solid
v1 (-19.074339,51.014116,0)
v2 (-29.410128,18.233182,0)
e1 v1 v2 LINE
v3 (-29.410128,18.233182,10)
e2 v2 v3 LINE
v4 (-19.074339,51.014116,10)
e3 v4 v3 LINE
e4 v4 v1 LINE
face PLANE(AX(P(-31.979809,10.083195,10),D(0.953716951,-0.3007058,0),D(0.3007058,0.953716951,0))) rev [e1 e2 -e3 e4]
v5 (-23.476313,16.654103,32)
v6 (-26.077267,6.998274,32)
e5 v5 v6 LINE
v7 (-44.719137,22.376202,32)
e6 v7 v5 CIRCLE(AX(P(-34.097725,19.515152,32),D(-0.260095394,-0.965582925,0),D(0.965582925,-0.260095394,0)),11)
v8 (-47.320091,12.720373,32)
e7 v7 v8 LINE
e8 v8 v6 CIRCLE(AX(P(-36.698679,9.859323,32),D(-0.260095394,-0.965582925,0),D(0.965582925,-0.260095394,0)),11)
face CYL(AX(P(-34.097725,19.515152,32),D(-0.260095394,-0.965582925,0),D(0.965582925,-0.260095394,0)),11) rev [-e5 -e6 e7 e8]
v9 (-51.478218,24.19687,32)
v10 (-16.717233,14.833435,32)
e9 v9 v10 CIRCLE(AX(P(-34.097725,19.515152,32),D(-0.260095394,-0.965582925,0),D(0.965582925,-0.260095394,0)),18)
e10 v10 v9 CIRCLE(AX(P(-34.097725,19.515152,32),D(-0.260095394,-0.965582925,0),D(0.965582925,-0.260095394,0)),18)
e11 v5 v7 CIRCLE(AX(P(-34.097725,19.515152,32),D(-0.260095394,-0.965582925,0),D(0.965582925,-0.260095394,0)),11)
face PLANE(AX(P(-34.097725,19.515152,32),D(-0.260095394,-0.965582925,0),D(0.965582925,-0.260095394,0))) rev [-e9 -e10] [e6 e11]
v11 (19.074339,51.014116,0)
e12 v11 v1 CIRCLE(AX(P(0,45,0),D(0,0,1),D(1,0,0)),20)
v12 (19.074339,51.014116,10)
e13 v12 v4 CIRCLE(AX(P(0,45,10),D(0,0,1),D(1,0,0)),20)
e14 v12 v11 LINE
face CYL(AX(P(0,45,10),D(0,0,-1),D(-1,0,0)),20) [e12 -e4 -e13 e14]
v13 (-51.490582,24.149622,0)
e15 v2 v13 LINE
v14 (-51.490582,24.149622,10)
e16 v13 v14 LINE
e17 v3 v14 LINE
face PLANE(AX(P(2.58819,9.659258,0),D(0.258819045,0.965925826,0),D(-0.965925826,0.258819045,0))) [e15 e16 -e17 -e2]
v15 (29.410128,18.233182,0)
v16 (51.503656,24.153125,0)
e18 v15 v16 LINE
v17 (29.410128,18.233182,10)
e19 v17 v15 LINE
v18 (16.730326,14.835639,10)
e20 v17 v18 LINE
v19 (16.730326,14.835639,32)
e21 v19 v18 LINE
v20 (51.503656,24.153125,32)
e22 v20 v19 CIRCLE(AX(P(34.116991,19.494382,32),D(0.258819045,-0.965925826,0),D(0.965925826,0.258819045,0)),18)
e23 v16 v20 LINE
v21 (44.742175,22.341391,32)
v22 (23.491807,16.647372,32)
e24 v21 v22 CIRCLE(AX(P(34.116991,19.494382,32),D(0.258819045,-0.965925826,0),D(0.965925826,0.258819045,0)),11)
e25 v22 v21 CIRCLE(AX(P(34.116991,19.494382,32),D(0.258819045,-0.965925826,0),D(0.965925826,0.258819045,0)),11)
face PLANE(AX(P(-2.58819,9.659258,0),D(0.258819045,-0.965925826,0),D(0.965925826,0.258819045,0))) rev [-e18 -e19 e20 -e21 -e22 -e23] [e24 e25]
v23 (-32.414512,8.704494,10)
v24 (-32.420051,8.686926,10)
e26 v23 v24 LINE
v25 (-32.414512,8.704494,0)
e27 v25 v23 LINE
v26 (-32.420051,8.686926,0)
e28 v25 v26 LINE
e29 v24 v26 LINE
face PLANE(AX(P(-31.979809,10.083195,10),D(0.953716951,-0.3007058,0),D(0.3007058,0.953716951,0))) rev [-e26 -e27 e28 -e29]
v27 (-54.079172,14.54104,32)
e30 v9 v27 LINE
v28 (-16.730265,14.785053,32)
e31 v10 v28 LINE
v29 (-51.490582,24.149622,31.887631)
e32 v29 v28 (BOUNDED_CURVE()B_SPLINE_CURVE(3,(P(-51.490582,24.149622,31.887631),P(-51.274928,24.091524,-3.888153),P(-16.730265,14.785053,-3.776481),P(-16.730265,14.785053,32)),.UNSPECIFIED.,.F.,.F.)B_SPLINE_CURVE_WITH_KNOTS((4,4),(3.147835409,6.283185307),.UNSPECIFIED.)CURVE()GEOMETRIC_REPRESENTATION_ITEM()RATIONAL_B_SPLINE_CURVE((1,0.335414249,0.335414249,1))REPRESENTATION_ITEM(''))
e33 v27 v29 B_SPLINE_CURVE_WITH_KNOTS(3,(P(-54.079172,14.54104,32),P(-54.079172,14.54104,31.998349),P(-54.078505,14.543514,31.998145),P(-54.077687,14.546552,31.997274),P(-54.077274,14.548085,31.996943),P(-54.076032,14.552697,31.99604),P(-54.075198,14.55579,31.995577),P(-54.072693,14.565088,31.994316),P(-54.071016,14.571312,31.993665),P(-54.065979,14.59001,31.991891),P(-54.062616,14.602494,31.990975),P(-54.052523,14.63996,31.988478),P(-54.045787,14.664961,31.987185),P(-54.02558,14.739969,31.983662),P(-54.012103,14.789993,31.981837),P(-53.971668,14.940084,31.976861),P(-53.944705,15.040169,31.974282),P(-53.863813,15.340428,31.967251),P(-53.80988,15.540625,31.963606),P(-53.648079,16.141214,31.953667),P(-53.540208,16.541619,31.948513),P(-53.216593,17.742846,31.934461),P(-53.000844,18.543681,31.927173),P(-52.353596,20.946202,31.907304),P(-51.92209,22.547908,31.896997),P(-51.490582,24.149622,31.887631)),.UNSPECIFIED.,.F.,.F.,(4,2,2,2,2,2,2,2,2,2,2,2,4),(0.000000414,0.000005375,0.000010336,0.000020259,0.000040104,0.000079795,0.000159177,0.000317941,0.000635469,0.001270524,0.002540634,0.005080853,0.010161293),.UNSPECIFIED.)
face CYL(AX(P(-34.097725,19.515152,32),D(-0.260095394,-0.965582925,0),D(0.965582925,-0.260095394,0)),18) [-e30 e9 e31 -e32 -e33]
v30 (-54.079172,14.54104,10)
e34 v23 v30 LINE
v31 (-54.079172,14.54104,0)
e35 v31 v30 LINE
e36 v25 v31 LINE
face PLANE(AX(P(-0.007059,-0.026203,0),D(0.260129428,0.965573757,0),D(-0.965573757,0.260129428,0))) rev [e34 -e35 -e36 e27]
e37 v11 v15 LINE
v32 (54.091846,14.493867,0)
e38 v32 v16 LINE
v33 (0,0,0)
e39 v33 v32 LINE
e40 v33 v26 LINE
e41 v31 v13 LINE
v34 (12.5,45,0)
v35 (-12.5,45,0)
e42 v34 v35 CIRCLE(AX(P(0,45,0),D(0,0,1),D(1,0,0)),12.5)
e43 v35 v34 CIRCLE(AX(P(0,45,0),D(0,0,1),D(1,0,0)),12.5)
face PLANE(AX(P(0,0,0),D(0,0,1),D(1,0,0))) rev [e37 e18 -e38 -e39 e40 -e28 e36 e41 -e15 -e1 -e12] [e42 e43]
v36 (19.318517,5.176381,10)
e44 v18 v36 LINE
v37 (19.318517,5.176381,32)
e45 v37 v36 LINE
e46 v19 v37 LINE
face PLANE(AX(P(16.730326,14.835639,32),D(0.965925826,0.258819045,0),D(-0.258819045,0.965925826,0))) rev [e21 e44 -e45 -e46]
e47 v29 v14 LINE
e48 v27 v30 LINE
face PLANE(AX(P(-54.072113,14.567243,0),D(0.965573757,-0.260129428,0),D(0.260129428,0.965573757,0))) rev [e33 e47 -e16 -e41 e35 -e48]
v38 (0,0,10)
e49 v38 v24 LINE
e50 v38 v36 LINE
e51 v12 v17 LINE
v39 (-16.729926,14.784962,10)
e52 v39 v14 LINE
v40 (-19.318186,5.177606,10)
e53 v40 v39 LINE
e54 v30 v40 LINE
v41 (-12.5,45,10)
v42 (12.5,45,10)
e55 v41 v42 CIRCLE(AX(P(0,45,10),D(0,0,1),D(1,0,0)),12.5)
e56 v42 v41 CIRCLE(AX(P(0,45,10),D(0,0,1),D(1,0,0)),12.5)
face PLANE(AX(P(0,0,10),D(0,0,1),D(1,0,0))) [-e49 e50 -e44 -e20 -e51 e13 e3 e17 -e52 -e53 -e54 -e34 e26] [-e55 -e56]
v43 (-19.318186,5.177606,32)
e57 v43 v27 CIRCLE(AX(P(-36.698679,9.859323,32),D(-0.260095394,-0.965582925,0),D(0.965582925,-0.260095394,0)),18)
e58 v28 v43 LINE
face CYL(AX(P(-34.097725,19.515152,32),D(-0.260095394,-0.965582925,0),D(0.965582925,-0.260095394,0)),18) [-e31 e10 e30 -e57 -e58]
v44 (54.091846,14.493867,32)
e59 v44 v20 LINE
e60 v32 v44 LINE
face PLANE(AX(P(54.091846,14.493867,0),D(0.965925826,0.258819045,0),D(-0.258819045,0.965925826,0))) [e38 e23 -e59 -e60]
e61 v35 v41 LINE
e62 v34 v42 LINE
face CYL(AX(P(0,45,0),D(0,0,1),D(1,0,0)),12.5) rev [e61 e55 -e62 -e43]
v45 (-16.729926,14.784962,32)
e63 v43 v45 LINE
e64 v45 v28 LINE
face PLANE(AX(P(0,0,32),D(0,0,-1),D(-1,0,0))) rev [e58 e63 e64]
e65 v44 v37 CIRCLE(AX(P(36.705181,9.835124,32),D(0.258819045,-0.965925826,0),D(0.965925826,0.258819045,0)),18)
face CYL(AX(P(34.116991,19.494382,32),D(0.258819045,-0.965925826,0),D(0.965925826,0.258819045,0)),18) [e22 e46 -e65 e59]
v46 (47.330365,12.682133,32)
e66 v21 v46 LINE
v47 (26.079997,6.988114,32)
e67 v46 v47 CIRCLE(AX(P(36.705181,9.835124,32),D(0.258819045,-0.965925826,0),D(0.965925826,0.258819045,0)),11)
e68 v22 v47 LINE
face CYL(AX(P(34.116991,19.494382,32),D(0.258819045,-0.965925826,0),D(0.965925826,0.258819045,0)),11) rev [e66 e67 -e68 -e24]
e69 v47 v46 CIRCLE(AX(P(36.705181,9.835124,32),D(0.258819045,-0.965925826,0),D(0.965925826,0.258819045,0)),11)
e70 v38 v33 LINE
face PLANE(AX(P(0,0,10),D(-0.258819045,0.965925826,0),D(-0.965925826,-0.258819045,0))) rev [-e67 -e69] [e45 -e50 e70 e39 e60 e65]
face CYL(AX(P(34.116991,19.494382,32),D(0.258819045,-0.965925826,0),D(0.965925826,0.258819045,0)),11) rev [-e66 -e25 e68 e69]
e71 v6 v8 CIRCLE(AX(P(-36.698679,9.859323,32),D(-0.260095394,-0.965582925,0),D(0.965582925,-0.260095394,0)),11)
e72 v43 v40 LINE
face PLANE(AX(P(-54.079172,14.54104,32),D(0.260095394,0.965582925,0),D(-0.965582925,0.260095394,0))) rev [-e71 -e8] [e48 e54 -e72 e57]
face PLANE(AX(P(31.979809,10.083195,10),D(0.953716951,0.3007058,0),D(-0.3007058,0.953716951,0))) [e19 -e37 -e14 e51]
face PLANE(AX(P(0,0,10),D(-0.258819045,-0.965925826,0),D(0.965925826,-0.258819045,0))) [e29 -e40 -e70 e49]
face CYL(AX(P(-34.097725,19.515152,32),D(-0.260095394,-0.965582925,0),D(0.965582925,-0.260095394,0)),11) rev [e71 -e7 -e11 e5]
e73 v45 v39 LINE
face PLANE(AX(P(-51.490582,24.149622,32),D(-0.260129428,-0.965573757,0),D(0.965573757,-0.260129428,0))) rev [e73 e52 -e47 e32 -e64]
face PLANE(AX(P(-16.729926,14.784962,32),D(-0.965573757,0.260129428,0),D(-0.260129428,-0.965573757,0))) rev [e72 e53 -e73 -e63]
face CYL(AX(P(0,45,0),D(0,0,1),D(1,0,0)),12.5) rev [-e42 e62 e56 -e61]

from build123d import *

# Parameters (mm, degrees)
LUG_PLATE_DEPTH          = 10
FLANGE_BASE_DEPTH        = 10
ANGLED_FLANGE_ARMS_DEPTH = 22
EYE_BOSS_A_SKETCH_R      = 18.000000011
EYE_BOSS_A_DEPTH         = 10
EYE_BOSS_B_SKETCH_R      = 18
EYE_BOSS_B_DEPTH         = 10
EYE_HOLE_A_22_SKETCH_R   = 11
EYE_HOLE_A_22_DEPTH      = 10
EYE_HOLE_B_22_SKETCH_R   = 11
EYE_HOLE_B_22_DEPTH      = 10
LUG_BORE_25_SKETCH_R     = 12.5
LUG_BORE_25_DEPTH        = 10


with BuildPart() as part:
    # Lug Plate Sketch → Lug Plate (new body)
    with BuildSketch(Plane.XY):
        with BuildLine():
            Line((-19.074339015, 51.01411599), (-32.420050634, 8.686926386))
            Line((-32.420050634, 8.686926386), (0, 0))
            Line((0, 0), (32.420050634, 8.686926386))
            Line((32.420050634, 8.686926386), (19.074339015, 51.01411599))
            ThreePointArc((19.074339015, 51.01411599), (0, 65), (-19.074339015, 51.01411599))
        make_face()
    extrude(amount=LUG_PLATE_DEPTH)

    # Flange Base Sketch → Flange Base (add)
    with BuildSketch(Plane.XY.offset(10)):
        Polygon((-54.079171789, 14.541040303), (-32.414511502, 8.704494269), (-29.410127859, 18.233181813), (-51.490581609, 24.149621564), align=None)
        Polygon((-32.414511502, 8.704494269), (-19.318516526, 5.176380902), (-16.730326075, 14.835639165), (-29.410127859, 18.233181813), align=None)
        Polygon((16.730326075, 14.835639165), (19.318516526, 5.176380902), (32.420050634, 8.686926386), (29.410127859, 18.233181813), align=None)
        Polygon((29.410127859, 18.233181813), (32.420050634, 8.686926386), (54.091846272, 14.493866526), (51.503655821, 24.153124789), align=None)
    extrude(amount=-FLANGE_BASE_DEPTH)

    # Angled Flange Arms Sketch → Angled Flange Arms (add)
    with BuildSketch(Plane.XY.offset(10)):
        Polygon((-51.490581609, 24.149621564), (-16.729926347, 14.784962163), (-19.318186451, 5.177606105), (-54.079171789, 14.541040303), align=None)
        Polygon((51.503655821, 24.153124789), (16.730326075, 14.835639165), (19.318516526, 5.176380902), (54.091846272, 14.493866526), align=None)
    extrude(amount=ANGLED_FLANGE_ARMS_DEPTH)

    # Eye Boss A Sketch → Eye Boss A (add)
    with BuildSketch(Plane(origin=(-0.006544851, -0.024297225, 0), x_dir=(0.965582925438563, -0.2600953942335516, 0), z_dir=(-0.2600953942335516, -0.9655829254385631, 0))):
        with Locations((-37.9999825, 32)):
            Circle(EYE_BOSS_A_SKETCH_R)
    extrude(amount=-EYE_BOSS_A_DEPTH)

    # Eye Boss B Sketch → Eye Boss B (add)
    with BuildSketch(Plane(origin=(0, 0, 0), x_dir=(0.9659258262890681, 0.25881904510252146, 0), z_dir=(0.25881904510252146, -0.9659258262890681, 0))):
        with Locations((38, 32)):
            Circle(EYE_BOSS_B_SKETCH_R)
    extrude(amount=-EYE_BOSS_B_DEPTH)

    # Eye Hole A _22 Sketch → Eye Hole A _22 (cut)
    with BuildSketch(Plane(origin=(-0.006544851, -0.024297225, 0), x_dir=(0.965582925438563, -0.2600953942335516, 0), z_dir=(-0.2600953942335516, -0.9655829254385631, 0))):
        with Locations((-37.9999825, 32)):
            Circle(EYE_HOLE_A_22_SKETCH_R)
    extrude(amount=-EYE_HOLE_A_22_DEPTH, mode=Mode.SUBTRACT)

    # Eye Hole B _22 Sketch → Eye Hole B _22 (cut)
    with BuildSketch(Plane(origin=(0, 0, 0), x_dir=(0.9659258262890681, 0.25881904510252146, 0), z_dir=(0.25881904510252146, -0.9659258262890681, 0))):
        with Locations((38, 32)):
            Circle(EYE_HOLE_B_22_SKETCH_R)
    extrude(amount=-EYE_HOLE_B_22_DEPTH, mode=Mode.SUBTRACT)

    # Lug Bore _25 Sketch → Lug Bore _25 (cut)
    with BuildSketch(Plane.XY.offset(10)):
        with Locations((0, 45)):
            Circle(LUG_BORE_25_SKETCH_R)
    extrude(amount=-LUG_BORE_25_DEPTH, mode=Mode.SUBTRACT)


solid = part.part
